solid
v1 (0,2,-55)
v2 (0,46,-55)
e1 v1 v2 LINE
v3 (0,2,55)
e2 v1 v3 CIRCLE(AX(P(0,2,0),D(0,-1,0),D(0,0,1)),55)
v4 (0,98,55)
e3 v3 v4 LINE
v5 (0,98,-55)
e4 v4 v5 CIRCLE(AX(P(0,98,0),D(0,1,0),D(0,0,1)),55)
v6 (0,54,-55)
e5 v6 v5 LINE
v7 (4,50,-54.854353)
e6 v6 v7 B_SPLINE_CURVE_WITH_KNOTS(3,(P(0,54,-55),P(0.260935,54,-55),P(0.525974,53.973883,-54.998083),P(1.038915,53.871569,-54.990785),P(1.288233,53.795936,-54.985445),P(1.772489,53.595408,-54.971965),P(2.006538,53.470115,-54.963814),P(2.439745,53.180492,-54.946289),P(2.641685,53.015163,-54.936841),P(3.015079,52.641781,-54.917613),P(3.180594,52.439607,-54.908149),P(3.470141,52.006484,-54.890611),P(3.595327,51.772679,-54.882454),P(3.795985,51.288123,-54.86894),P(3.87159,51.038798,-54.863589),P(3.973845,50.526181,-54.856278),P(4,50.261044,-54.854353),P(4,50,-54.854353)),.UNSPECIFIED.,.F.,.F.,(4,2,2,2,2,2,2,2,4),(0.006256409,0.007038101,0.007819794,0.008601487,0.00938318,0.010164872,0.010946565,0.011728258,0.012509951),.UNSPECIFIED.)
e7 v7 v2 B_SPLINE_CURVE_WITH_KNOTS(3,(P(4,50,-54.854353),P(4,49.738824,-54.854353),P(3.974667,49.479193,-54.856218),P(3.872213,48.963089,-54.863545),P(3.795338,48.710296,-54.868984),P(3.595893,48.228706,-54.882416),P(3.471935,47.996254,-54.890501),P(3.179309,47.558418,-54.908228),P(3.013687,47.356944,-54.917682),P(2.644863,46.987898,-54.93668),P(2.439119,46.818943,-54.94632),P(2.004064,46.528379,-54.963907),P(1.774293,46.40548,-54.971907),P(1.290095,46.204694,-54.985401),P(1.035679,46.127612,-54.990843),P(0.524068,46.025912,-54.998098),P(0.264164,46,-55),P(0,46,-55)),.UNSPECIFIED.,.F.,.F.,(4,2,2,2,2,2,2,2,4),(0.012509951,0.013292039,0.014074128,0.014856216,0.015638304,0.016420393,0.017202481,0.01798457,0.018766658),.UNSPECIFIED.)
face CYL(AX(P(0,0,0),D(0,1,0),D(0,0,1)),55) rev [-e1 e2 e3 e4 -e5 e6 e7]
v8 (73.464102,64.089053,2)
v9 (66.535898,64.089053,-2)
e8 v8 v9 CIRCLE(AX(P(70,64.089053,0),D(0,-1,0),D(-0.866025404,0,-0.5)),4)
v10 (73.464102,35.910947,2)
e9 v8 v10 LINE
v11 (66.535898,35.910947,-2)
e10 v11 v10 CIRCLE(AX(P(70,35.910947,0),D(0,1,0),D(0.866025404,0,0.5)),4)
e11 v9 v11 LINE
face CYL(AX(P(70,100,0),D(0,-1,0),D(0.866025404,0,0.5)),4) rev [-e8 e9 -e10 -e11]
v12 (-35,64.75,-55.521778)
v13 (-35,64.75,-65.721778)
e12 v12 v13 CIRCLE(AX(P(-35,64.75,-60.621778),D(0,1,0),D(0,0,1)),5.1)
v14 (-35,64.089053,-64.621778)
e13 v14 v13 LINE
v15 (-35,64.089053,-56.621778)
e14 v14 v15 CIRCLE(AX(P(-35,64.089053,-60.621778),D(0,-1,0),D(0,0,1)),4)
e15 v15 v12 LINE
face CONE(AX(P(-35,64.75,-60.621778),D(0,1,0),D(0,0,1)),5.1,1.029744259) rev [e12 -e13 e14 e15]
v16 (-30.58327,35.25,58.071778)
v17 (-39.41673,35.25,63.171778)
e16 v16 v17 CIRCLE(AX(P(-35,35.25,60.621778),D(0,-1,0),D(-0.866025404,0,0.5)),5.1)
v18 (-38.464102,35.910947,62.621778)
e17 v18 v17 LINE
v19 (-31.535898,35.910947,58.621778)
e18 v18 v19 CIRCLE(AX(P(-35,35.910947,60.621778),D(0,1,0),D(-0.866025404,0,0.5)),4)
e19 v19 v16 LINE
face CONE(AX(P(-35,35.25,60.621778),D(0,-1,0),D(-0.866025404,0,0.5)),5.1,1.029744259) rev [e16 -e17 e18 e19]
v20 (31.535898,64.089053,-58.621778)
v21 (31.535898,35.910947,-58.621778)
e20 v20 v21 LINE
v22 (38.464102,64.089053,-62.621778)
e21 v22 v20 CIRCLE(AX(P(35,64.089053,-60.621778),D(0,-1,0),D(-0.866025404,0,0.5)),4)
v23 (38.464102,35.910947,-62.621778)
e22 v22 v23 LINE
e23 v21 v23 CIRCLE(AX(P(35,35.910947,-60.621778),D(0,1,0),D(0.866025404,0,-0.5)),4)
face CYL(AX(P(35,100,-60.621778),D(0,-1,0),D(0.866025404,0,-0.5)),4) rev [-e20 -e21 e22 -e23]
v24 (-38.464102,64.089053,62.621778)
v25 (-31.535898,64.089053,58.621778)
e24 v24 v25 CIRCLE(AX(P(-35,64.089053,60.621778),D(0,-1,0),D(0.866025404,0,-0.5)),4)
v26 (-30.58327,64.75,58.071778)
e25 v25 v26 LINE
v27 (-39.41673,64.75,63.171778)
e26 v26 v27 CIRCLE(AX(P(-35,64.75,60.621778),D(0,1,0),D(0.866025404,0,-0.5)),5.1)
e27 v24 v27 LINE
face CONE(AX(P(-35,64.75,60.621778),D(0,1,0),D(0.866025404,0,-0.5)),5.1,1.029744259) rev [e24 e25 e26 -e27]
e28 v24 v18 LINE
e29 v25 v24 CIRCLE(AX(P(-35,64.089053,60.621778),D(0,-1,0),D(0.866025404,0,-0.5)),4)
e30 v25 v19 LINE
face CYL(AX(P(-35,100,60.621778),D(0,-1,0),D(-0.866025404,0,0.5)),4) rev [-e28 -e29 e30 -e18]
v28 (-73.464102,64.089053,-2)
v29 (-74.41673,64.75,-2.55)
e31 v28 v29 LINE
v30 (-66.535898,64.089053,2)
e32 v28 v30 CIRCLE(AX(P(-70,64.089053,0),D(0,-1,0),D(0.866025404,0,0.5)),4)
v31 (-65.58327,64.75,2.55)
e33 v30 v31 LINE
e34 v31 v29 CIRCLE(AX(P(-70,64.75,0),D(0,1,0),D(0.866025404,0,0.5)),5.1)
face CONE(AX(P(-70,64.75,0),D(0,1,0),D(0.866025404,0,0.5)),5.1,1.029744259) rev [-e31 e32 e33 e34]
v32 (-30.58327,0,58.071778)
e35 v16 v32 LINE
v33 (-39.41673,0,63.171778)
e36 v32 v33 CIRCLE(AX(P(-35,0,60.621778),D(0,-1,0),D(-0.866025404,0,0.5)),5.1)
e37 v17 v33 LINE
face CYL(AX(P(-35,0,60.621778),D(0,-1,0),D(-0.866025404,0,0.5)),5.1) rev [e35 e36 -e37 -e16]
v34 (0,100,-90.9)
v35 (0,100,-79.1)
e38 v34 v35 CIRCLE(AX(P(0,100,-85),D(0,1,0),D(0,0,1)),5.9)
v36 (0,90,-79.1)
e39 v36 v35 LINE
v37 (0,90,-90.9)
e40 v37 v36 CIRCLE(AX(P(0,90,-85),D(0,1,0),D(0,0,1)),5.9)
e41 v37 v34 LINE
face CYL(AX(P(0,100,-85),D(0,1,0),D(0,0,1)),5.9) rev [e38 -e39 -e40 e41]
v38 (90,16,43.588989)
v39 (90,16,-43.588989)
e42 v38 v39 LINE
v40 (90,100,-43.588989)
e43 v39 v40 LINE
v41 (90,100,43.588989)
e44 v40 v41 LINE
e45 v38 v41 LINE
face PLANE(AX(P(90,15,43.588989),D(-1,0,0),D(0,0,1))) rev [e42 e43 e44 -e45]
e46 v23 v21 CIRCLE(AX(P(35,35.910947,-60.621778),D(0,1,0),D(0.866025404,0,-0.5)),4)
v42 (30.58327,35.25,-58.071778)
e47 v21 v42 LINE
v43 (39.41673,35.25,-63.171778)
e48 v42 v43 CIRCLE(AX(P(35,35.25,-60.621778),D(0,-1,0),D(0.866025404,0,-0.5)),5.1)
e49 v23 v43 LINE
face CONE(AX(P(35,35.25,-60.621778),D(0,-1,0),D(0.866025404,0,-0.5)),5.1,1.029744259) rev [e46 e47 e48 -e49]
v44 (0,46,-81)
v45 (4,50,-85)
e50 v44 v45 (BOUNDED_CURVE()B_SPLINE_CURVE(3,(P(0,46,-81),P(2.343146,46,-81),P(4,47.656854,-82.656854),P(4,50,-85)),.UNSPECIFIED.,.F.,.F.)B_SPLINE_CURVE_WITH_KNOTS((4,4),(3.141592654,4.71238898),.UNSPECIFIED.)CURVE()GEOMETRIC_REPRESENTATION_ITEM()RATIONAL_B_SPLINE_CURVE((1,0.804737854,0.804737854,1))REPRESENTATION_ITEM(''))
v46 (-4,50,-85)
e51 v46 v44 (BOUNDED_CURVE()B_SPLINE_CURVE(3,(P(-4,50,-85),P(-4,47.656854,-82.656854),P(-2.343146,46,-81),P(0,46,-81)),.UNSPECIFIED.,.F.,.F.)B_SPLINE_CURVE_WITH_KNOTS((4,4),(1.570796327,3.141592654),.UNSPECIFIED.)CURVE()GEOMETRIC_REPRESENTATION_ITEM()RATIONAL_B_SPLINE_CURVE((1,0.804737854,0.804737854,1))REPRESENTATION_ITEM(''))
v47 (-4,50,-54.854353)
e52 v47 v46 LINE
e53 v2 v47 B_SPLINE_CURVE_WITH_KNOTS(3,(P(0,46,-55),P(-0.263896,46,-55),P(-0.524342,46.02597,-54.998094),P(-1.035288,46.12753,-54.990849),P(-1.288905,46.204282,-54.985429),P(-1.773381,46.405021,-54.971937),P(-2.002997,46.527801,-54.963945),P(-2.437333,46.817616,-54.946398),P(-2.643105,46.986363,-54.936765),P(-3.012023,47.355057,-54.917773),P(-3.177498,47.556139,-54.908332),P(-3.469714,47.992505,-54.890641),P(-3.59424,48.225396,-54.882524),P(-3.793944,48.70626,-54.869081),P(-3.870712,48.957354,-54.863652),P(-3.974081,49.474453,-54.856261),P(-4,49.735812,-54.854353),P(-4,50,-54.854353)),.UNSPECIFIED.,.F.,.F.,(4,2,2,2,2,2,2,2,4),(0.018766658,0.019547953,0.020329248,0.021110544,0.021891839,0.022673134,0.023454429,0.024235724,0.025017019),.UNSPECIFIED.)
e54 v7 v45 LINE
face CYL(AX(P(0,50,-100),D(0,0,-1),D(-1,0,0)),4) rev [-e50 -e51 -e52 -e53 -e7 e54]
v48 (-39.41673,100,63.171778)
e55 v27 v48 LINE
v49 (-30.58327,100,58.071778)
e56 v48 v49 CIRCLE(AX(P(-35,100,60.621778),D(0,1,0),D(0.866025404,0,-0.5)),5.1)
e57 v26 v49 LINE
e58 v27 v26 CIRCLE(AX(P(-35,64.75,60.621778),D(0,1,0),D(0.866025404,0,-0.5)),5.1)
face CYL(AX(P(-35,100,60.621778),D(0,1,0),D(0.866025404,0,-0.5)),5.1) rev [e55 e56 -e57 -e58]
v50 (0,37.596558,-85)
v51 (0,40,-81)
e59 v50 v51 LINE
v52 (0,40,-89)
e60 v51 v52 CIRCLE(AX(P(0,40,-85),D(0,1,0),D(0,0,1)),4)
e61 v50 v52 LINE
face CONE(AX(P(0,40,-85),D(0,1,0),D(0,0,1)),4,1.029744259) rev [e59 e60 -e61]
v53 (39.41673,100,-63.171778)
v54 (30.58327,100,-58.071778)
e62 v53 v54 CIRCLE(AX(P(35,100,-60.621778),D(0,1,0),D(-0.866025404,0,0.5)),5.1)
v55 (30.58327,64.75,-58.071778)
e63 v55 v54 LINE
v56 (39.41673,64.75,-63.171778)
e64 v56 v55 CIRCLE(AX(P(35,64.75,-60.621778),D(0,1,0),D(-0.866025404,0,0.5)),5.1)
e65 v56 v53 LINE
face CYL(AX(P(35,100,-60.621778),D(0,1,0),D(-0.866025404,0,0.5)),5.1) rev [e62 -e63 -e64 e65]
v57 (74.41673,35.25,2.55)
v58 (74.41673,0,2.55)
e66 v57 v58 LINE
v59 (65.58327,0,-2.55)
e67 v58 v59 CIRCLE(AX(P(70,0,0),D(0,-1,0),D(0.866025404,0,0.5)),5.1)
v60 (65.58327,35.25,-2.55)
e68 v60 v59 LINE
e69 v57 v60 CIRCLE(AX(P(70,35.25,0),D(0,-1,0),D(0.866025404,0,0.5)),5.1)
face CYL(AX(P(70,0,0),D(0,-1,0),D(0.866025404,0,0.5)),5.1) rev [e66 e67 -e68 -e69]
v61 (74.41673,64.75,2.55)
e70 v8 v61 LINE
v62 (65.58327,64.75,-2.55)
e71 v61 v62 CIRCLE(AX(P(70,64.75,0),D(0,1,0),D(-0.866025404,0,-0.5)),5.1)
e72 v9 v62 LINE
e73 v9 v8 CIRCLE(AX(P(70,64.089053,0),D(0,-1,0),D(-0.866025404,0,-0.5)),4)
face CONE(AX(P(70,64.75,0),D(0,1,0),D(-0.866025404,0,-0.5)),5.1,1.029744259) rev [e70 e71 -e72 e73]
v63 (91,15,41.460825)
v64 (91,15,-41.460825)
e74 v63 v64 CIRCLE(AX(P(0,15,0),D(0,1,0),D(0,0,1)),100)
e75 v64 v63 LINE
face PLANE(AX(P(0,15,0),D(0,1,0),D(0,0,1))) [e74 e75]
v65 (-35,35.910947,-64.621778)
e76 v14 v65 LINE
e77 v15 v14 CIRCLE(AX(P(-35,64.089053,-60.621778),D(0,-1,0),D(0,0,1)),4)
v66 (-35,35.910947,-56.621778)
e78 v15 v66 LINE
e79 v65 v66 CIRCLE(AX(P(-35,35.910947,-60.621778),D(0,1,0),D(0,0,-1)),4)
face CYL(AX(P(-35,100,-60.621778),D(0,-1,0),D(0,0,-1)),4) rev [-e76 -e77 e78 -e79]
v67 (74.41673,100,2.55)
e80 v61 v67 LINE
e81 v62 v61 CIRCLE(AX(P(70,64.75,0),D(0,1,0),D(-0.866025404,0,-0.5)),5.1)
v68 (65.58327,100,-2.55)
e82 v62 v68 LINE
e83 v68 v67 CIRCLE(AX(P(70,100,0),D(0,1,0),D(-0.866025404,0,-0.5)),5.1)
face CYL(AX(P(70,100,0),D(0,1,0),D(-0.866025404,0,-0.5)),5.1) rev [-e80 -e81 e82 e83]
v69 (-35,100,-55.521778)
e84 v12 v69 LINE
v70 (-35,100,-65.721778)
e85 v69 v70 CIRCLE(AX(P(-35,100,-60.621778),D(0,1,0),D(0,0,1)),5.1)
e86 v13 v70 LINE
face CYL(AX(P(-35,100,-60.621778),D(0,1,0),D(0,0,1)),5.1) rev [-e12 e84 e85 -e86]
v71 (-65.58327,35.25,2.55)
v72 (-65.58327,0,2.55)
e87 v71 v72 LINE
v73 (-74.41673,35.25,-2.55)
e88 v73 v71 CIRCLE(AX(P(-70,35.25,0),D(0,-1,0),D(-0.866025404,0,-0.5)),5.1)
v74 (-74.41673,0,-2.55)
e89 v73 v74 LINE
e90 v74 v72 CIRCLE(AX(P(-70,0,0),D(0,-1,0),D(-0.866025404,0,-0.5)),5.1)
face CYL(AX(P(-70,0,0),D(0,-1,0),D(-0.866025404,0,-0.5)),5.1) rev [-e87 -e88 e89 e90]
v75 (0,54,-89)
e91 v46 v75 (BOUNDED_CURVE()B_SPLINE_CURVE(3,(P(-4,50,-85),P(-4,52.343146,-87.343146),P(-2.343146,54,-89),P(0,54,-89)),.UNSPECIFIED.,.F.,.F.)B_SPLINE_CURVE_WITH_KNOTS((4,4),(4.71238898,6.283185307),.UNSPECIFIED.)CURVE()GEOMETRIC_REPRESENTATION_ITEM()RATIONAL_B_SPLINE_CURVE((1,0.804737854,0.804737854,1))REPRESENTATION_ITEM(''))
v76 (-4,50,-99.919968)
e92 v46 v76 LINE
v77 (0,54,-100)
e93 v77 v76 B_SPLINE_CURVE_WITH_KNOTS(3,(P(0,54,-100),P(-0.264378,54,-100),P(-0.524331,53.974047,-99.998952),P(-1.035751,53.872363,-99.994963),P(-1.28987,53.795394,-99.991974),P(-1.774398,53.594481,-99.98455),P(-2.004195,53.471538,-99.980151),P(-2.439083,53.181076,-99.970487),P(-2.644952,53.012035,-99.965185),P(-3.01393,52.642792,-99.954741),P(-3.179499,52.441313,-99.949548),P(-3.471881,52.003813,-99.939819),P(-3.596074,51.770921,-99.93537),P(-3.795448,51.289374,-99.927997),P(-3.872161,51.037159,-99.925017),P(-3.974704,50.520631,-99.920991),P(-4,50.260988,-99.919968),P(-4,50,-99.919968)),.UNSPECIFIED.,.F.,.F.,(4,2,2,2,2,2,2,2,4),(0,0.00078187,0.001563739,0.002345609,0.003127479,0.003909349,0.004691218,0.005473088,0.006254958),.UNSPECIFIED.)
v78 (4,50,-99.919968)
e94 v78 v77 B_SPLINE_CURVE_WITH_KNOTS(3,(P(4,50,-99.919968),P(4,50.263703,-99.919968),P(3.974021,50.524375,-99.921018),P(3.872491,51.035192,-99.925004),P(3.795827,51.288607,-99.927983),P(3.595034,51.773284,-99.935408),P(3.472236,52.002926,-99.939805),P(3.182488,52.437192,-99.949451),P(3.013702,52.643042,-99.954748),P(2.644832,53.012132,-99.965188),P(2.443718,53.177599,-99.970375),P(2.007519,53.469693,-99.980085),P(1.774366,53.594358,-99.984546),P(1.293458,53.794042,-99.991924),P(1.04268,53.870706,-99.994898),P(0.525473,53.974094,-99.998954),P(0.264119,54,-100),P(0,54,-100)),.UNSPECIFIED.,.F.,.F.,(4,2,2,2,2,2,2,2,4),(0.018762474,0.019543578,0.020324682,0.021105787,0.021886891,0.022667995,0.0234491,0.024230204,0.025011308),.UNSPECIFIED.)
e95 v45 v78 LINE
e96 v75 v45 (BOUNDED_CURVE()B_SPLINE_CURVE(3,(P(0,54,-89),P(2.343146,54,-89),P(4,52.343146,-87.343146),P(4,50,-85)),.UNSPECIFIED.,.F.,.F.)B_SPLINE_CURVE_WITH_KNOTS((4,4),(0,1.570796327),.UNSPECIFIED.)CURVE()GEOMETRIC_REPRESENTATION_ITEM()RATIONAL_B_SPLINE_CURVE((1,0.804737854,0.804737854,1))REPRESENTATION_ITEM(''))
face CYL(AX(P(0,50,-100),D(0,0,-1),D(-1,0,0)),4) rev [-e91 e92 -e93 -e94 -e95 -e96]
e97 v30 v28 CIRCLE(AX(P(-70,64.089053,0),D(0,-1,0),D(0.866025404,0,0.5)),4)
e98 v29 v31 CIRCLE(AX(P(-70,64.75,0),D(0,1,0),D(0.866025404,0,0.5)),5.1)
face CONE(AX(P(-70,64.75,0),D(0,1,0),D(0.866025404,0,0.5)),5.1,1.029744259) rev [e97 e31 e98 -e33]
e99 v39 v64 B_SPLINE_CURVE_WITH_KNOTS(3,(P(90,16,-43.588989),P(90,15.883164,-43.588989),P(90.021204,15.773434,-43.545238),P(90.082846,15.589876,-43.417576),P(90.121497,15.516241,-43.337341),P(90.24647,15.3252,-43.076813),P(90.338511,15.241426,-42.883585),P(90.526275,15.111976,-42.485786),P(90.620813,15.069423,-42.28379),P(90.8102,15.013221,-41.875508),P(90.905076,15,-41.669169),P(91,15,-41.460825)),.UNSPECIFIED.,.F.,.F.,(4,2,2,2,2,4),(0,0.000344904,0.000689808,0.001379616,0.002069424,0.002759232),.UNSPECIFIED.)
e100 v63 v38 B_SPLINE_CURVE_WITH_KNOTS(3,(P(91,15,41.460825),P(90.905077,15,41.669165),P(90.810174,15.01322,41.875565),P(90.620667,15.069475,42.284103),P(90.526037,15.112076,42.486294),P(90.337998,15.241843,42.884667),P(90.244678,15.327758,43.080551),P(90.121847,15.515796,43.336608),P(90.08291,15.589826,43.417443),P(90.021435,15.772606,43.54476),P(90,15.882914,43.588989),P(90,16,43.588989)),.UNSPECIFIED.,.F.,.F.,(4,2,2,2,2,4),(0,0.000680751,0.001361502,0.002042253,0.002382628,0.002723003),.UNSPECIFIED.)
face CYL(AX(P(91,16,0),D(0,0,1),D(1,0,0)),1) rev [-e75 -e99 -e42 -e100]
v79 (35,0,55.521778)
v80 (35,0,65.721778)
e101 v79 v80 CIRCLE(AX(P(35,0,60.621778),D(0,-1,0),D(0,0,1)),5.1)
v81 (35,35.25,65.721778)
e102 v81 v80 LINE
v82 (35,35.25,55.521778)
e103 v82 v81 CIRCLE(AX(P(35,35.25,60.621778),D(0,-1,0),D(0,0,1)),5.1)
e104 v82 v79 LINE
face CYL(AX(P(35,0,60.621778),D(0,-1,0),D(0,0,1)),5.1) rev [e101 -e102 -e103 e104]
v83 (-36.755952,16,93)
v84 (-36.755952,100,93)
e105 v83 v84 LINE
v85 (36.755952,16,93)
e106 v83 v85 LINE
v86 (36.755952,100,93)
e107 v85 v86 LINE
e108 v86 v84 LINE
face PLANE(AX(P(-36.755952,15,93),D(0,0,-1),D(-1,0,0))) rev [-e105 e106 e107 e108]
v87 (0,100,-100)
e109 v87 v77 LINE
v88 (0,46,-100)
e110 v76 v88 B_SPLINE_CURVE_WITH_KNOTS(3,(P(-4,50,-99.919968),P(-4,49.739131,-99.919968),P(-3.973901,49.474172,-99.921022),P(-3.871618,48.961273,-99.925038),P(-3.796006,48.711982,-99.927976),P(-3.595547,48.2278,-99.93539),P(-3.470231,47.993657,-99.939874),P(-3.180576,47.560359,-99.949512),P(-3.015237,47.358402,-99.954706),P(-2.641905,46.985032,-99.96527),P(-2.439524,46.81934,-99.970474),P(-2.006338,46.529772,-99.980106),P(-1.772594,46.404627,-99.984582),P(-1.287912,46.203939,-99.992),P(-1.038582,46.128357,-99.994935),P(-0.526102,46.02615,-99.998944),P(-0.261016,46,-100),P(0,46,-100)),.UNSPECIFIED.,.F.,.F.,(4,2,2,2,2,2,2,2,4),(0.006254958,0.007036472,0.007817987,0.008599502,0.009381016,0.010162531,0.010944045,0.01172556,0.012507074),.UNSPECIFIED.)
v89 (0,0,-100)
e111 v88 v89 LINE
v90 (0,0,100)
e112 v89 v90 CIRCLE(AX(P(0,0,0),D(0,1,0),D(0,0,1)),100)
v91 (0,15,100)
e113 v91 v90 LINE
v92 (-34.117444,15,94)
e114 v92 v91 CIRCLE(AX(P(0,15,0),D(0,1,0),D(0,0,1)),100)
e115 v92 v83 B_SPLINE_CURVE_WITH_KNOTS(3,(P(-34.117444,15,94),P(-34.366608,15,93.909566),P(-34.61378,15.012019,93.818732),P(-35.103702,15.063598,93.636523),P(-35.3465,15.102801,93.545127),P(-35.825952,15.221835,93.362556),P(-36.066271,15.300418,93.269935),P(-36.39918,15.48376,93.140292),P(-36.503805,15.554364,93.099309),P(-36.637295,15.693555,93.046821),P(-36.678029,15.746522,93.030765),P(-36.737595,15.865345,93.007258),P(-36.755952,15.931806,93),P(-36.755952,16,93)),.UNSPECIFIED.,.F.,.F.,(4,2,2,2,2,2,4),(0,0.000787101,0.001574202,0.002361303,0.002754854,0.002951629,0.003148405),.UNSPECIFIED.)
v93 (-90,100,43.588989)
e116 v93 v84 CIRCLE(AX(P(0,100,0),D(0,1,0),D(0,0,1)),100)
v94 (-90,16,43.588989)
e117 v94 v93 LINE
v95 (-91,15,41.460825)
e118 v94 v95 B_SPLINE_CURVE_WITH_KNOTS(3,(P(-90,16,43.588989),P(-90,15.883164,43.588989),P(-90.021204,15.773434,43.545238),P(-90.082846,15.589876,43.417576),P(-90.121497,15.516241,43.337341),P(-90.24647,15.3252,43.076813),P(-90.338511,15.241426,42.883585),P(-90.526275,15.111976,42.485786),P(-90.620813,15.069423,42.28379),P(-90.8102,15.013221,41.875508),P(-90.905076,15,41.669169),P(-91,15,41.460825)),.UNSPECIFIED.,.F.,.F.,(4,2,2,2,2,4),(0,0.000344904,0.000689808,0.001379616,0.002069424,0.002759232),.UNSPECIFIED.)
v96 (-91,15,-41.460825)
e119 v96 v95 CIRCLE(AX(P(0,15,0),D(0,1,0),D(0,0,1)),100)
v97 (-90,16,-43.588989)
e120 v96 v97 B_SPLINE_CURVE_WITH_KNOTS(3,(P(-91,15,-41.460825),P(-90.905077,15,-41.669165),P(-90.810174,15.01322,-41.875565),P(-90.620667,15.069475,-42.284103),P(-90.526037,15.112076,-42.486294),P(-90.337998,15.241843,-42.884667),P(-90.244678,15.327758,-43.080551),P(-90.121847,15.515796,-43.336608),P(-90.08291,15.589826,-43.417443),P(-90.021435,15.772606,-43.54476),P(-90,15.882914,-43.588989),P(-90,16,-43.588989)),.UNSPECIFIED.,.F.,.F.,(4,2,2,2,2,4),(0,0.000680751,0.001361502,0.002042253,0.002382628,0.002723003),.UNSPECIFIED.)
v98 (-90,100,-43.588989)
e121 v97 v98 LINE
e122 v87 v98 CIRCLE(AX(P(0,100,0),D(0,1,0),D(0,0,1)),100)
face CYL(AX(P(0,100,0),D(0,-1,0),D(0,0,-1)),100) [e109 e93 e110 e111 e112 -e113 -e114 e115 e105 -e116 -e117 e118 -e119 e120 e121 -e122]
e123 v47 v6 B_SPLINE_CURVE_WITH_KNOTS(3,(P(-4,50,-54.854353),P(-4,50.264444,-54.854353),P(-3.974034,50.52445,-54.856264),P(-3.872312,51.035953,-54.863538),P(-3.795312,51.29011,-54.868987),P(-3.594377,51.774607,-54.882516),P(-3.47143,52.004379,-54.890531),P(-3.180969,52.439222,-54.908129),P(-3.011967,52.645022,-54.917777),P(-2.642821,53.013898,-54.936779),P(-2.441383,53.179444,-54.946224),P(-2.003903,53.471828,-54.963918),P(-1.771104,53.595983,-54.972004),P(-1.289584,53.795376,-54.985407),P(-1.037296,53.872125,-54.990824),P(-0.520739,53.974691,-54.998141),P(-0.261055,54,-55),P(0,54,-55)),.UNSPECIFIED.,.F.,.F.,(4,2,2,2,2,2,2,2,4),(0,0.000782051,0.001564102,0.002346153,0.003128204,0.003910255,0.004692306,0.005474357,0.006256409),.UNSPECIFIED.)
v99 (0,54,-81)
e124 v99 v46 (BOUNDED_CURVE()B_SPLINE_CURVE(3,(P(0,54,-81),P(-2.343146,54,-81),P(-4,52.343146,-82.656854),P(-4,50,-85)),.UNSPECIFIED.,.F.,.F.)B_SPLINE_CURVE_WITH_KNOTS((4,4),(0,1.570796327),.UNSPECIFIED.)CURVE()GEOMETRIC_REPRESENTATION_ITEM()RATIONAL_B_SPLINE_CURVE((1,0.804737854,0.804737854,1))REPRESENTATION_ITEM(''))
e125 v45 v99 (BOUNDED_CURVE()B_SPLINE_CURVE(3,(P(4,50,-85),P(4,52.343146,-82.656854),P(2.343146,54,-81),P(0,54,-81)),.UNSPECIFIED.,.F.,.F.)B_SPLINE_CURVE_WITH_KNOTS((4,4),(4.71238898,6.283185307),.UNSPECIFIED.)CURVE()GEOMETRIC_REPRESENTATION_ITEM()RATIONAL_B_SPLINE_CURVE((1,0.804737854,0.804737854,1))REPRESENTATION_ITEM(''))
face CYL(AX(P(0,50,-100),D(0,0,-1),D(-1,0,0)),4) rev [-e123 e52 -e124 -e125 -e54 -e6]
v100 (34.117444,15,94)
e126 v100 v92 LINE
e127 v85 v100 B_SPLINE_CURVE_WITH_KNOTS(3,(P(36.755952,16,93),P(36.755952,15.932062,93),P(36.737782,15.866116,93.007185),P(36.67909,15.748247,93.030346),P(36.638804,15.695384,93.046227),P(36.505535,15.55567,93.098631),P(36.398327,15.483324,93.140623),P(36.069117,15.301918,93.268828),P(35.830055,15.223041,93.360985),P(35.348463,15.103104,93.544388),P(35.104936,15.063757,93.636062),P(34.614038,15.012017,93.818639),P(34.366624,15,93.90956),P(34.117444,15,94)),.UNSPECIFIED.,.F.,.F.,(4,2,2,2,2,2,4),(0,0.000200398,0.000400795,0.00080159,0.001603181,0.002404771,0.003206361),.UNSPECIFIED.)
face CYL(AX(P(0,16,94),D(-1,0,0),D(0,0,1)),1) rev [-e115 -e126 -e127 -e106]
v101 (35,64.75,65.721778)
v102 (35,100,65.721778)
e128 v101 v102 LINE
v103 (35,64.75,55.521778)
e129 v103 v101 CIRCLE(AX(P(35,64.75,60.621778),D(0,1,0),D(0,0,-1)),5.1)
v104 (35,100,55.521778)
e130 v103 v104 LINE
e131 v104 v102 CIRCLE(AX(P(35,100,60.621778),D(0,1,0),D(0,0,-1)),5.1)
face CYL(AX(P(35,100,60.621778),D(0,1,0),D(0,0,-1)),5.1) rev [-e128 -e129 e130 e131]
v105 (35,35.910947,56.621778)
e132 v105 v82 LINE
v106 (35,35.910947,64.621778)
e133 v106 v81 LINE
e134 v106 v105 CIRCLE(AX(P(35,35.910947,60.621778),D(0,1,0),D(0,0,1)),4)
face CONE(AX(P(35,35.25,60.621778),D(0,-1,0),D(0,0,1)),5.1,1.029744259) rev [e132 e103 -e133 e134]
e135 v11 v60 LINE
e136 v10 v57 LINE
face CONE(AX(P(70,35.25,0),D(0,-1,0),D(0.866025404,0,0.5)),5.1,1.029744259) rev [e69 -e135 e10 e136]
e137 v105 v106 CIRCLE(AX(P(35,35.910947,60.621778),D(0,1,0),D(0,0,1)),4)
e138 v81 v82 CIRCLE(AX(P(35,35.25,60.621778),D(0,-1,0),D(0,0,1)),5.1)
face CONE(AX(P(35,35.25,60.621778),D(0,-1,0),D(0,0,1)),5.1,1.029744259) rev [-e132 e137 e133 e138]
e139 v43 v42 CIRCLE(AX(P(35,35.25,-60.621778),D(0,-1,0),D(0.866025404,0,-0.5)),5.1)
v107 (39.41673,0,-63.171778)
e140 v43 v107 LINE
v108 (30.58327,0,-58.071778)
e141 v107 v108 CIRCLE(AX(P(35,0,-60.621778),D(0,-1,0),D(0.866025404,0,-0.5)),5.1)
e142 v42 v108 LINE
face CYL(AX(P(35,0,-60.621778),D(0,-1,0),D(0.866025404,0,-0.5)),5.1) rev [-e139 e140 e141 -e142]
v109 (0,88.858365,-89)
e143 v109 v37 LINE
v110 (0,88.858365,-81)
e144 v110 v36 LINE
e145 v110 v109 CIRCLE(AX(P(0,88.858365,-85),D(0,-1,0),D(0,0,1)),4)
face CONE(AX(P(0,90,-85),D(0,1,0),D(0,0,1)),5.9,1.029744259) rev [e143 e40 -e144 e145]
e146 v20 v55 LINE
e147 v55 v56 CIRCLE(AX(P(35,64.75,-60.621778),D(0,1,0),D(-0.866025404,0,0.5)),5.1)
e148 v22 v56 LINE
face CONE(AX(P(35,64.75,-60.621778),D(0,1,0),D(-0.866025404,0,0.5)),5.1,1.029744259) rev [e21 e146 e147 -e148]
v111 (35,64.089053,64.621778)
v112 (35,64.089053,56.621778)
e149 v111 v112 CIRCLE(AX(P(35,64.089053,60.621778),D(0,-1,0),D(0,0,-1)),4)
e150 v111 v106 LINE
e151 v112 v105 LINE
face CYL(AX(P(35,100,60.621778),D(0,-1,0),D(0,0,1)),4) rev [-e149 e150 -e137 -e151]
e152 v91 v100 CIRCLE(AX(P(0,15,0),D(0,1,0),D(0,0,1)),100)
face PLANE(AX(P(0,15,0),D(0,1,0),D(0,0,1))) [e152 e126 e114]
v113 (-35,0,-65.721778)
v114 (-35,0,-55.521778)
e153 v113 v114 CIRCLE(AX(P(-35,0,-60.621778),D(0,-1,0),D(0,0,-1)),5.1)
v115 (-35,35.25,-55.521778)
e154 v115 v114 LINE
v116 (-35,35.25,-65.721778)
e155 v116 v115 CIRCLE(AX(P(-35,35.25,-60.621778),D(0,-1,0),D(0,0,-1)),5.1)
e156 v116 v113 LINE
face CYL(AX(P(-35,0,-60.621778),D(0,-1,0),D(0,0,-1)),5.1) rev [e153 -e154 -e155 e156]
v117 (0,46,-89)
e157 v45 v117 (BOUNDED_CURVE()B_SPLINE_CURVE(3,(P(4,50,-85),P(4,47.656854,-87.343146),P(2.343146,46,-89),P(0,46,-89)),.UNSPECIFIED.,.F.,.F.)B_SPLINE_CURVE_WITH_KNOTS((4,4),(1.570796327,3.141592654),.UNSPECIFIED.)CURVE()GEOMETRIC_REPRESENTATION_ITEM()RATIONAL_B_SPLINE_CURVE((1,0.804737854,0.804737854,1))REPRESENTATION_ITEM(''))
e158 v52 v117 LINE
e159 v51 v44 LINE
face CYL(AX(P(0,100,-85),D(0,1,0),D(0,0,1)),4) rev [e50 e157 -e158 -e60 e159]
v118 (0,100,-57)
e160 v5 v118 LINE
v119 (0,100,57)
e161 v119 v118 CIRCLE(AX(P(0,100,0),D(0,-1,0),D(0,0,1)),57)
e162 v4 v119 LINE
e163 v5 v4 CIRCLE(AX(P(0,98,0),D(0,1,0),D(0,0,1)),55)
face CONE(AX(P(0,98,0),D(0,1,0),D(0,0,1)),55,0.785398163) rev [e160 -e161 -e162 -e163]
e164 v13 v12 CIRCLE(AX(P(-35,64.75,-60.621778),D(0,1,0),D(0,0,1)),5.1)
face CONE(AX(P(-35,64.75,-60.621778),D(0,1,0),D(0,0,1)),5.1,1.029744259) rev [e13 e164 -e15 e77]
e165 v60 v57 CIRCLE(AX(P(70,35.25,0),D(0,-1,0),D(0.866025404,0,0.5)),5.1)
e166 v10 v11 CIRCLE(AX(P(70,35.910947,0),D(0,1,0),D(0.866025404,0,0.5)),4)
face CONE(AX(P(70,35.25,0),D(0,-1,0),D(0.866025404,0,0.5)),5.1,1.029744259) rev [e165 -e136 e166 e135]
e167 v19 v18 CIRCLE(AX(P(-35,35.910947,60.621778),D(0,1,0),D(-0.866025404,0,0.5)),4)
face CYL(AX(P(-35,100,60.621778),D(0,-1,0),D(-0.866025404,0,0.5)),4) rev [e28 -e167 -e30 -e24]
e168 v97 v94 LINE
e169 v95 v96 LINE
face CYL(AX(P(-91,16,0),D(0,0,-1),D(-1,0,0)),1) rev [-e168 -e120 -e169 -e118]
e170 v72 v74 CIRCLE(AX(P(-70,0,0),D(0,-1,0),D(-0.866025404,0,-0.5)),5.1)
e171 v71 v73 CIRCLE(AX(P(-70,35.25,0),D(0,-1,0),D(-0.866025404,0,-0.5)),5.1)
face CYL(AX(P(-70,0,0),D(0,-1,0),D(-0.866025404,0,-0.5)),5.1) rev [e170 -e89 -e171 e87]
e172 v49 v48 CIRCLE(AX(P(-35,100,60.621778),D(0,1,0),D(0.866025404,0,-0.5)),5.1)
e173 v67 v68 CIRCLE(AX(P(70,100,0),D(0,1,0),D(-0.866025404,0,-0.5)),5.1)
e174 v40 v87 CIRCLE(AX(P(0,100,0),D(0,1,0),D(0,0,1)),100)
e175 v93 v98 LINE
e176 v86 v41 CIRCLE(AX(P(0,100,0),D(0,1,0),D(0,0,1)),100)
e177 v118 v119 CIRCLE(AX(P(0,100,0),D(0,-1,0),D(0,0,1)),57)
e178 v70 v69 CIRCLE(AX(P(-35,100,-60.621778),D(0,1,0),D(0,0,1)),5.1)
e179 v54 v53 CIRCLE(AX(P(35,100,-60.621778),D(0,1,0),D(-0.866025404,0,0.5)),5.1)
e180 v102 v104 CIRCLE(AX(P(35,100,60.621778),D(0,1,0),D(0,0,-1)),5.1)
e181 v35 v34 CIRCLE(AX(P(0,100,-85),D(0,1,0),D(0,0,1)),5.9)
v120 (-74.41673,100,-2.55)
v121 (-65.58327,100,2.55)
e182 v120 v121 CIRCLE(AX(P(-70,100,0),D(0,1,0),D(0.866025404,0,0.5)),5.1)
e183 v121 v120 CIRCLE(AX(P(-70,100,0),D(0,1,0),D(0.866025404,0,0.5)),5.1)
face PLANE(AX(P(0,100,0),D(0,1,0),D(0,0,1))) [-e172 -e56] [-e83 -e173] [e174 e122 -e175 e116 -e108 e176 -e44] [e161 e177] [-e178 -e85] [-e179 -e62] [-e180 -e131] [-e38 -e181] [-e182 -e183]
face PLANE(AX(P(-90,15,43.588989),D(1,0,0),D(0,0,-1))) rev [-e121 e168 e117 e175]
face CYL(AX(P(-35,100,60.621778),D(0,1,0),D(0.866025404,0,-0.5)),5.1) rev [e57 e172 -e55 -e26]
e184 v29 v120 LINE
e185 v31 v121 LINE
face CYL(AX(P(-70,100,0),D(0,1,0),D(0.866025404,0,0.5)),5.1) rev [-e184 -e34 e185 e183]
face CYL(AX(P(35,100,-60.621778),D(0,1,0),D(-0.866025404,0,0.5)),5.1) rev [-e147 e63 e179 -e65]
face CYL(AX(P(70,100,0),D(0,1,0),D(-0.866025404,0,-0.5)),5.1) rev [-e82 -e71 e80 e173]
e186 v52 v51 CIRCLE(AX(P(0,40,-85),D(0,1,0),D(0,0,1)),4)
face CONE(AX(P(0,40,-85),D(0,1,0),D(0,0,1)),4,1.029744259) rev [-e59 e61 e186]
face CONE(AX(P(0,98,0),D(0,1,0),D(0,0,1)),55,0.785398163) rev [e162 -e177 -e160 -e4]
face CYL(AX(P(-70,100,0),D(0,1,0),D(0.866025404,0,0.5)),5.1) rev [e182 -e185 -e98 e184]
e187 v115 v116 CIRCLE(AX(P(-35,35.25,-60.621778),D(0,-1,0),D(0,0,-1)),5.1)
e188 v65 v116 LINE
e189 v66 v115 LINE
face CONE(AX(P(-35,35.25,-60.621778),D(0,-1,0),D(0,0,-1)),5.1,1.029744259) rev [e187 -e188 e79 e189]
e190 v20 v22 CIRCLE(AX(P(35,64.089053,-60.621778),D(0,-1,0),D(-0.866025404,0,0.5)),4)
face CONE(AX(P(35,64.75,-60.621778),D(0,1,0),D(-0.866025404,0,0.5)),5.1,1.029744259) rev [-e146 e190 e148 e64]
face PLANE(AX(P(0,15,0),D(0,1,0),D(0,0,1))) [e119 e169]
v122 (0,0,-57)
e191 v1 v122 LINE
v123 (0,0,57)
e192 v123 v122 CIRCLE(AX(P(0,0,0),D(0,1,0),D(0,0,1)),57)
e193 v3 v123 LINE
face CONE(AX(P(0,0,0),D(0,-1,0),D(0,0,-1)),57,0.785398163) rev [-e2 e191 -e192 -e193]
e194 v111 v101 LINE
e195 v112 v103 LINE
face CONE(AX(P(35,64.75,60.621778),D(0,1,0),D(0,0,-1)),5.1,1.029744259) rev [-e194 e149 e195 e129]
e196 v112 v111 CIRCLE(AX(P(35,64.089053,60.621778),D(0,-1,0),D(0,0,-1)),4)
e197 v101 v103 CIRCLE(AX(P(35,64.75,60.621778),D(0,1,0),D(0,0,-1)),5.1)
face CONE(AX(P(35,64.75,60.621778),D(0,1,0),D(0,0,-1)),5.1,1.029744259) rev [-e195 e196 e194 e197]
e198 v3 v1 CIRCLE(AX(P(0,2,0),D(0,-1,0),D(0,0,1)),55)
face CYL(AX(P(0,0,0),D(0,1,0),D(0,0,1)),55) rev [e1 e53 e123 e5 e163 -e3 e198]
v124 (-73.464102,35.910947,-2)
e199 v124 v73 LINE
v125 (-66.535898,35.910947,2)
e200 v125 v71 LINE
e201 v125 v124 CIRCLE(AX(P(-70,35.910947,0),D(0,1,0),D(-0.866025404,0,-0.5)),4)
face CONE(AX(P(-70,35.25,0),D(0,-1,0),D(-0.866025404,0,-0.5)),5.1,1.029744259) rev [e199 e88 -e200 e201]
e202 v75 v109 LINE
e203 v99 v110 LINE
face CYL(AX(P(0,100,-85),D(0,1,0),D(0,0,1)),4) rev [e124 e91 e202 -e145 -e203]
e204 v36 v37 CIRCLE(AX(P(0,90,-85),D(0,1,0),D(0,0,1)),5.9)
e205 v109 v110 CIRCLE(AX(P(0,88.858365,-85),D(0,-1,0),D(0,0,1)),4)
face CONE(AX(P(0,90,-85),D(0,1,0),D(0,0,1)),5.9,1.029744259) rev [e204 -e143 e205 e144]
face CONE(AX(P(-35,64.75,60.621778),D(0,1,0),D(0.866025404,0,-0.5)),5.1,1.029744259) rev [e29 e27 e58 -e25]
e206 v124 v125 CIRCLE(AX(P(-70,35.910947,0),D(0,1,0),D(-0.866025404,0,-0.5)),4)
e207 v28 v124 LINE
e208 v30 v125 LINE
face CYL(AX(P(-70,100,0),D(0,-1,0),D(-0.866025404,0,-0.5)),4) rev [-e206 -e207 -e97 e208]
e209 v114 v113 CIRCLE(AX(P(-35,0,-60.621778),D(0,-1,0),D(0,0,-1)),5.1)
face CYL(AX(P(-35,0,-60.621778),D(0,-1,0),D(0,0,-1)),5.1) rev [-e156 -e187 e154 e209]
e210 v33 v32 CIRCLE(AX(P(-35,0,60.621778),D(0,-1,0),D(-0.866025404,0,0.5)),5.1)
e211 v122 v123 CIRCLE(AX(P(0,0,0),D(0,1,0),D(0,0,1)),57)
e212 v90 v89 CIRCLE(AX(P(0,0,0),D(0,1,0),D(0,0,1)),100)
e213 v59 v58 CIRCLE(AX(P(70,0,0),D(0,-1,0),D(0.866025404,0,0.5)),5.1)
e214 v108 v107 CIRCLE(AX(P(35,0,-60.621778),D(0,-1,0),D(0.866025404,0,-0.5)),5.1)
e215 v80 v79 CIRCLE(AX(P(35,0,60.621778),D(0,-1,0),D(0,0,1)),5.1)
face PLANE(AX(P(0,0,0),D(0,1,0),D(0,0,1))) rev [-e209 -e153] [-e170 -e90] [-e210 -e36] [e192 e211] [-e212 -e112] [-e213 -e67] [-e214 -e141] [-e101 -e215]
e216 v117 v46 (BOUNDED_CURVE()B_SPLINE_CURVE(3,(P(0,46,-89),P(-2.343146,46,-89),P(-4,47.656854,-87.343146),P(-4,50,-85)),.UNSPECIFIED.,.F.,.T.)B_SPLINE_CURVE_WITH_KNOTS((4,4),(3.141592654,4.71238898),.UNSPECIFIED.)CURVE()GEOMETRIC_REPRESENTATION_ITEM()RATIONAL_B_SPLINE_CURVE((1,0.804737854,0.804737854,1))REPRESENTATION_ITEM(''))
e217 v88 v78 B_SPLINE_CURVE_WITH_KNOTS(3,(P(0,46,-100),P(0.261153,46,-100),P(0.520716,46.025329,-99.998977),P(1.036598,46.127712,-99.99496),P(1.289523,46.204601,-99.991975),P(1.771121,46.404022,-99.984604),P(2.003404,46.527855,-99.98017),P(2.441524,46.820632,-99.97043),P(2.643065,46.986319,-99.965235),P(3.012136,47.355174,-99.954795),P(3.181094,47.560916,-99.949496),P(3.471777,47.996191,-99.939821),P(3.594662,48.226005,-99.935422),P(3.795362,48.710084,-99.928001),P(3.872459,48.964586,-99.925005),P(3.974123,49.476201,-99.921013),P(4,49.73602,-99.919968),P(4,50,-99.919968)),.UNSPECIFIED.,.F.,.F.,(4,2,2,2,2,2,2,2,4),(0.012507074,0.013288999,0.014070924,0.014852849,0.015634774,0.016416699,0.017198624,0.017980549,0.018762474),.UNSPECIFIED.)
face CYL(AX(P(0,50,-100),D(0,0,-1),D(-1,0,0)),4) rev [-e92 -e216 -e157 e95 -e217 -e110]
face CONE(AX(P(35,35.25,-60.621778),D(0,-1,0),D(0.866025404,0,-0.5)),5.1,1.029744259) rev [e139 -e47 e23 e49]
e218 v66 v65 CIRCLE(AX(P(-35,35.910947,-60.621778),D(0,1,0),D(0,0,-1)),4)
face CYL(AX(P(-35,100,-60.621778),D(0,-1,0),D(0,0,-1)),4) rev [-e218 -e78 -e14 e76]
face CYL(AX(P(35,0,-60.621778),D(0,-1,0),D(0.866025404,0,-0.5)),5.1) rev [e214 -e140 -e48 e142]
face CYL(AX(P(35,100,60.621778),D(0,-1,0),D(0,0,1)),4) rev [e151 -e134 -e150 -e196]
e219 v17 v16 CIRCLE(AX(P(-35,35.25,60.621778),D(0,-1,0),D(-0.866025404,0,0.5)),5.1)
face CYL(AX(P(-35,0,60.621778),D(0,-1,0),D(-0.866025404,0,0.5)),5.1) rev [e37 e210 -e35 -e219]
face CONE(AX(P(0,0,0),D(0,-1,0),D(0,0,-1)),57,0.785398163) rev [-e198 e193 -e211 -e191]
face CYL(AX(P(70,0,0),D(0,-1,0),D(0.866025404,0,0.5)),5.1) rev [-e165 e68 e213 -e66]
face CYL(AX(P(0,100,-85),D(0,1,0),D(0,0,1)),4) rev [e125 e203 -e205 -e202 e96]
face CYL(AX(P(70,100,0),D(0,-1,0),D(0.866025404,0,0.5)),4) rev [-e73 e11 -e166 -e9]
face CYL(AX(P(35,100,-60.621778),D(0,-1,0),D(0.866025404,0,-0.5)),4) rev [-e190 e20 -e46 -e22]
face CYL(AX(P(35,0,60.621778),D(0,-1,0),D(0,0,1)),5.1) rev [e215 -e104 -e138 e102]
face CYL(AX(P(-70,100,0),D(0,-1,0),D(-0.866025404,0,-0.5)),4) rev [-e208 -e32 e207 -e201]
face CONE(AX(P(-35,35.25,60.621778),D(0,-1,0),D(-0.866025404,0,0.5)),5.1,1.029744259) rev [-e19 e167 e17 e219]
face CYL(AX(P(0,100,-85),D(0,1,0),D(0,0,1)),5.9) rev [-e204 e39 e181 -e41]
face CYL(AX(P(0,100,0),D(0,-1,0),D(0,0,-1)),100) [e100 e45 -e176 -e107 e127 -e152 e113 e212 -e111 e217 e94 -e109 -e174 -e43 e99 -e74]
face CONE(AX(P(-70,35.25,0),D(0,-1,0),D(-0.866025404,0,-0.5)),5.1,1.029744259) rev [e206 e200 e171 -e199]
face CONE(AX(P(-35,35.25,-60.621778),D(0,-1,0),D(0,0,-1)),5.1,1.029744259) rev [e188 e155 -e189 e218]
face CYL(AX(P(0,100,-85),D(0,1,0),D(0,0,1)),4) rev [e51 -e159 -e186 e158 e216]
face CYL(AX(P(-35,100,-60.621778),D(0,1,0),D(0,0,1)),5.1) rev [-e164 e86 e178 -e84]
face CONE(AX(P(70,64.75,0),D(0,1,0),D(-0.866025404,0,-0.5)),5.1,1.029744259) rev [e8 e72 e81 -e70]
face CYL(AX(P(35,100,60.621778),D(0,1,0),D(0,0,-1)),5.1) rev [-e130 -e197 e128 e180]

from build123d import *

# Parameters (mm, degrees)
SKETCH1_R                    = 100
BOSS_EXTRUDE1_DEPTH          = 100
CUT_EXTRUDE1_START           = -85
CUT_EXTRUDE1_DEPTH           = 85
SKETCH3_R                    = 55
CUT_EXTRUDE2_DEPTH           = 174.205080757
CHAMFER1_SIZE                = 2
SKETCH10_R                   = 4
CUT_EXTRUDE3_DEPTH           = 174.205080757
CIRPATTERN1_COUNT            = 6
G1_4_TAPPED_HOLE1_D          = 11.8
G1_4_TAPPED_HOLE1_DEPTH      = 10
G1_4_TAPPED_HOLE1_TIP        = 3.545077652
F_8_0_8_DIAMETER_HOLE1_D     = 8
F_8_0_8_DIAMETER_HOLE1_DEPTH = 60
F_8_0_8_DIAMETER_HOLE1_TIP   = 2.403442476
F_8_0_8_DIAMETER_HOLE2_D     = 8
F_8_0_8_DIAMETER_HOLE2_DEPTH = 60
F_8_0_8_DIAMETER_HOLE2_TIP   = 2.403442476
FILLET1_R                    = 1


with BuildPart() as part:
    # Sketch1 → Boss-Extrude1 (new body)
    with BuildSketch(Plane(origin=(0, 0, 0), x_dir=(1, 0, 0), z_dir=(0, 1, 0))):
        with Locations(Location((0, 0, 0), (0, 0, 270))):
            Circle(SKETCH1_R)
    extrude(amount=BOSS_EXTRUDE1_DEPTH)

    # Sketch2 → Cut-Extrude1 (cut)
    with BuildSketch(Plane(origin=(0, 100, 0), x_dir=(1, 0, 0), z_dir=(0, 1, 0)).offset(CUT_EXTRUDE1_START)):
        with BuildLine():
            Line((-36.755951899, -93), (36.755951899, -93))
            ThreePointArc((36.755951899, -93), (0, -100), (-36.755951899, -93))
        make_face()
        with BuildLine():
            Line((-90, -43.588989435), (-90, 43.588989435))
            ThreePointArc((-90, 43.588989435), (-100, 0), (-90, -43.588989435))
        make_face()
        with BuildLine():
            Line((90, -43.588989435), (90, 43.588989435))
            ThreePointArc((90, 43.588989435), (100, 0), (90, -43.588989435))
        make_face()
    extrude(amount=CUT_EXTRUDE1_DEPTH, mode=Mode.SUBTRACT)

    # Sketch3 → Cut-Extrude2 (cut, through all)
    with BuildSketch(Plane(origin=(0, 100, 0), x_dir=(1, 0, 0), z_dir=(0, 1, 0))):
        with Locations(Location((0, 0, 0), (0, 0, 270))):
            Circle(SKETCH3_R)
    extrude(amount=-CUT_EXTRUDE2_DEPTH, mode=Mode.SUBTRACT)

    # Chamfer1
    chamfer1_edges = [part.edges().sort_by_distance(p)[0] for p in [
        (0, 0, -55),
        (0, 100, -55),
    ]]
    chamfer(chamfer1_edges, length=CHAMFER1_SIZE)

    # Sketch6 → M12 Tapped Hole1 (revolve, cut)
    with BuildSketch(Plane(origin=(-35, 100, -60.621778265), x_dir=(0, 0, 1), z_dir=(1, 0, 0))):
        Polygon((0, 0), (0, 38.314389157), (5.1, 35.25), (5.1, 0), align=None)
    m12_tapped_hole1 = revolve(axis=Axis((-35, 106.35, -60.621778265), (0, -1, 0)), mode=Mode.SUBTRACT)

    # Sketch9 → M12 Tapped Hole2 (revolve, cut)
    with BuildSketch(Plane(origin=(-35, 0, -60.621778265), x_dir=(0, 0, -1), z_dir=(1, 0, 0))):
        Polygon((0, 0), (0, 38.314389157), (5.1, 35.25), (5.1, 0), align=None)
    m12_tapped_hole2 = revolve(axis=Axis((-35, -6.35, -60.621778265), (0, 1, 0)), mode=Mode.SUBTRACT)

    # Sketch10 → Cut-Extrude3 (cut, through all)
    with BuildSketch(Plane.XZ):
        with Locations(Location((-35, -60.621778265, 0), (0, 0, 270))):
            Circle(SKETCH10_R)
    cut_extrude3 = extrude(amount=-CUT_EXTRUDE3_DEPTH, mode=Mode.SUBTRACT)

    # CirPattern1: M12 Tapped Hole1, M12 Tapped Hole2, Cut-Extrude3 ×6 about axis
    cirpattern1_axis = Axis((0, 0, 0), (0, 1, 0))
    add([m12_tapped_hole1.rotate(cirpattern1_axis, i * 360 / CIRPATTERN1_COUNT) for i in range(1, CIRPATTERN1_COUNT)], mode=Mode.SUBTRACT)
    add([m12_tapped_hole2.rotate(cirpattern1_axis, i * 360 / CIRPATTERN1_COUNT) for i in range(1, CIRPATTERN1_COUNT)], mode=Mode.SUBTRACT)
    add([cut_extrude3.rotate(cirpattern1_axis, i * 360 / CIRPATTERN1_COUNT) for i in range(1, CIRPATTERN1_COUNT)], mode=Mode.SUBTRACT)

    # G1/4 Tapped Hole1
    with Locations(Plane(origin=(0, 100, 0), x_dir=(1, 0, 0), z_dir=(0, 1, 0))):
        with Locations((0, 85)):
            Hole(G1_4_TAPPED_HOLE1_D / 2, depth=G1_4_TAPPED_HOLE1_DEPTH)
            with Locations((0, 0, -(G1_4_TAPPED_HOLE1_DEPTH + G1_4_TAPPED_HOLE1_TIP / 2))):  # 118° drill point
                Cone(0, G1_4_TAPPED_HOLE1_D / 2, G1_4_TAPPED_HOLE1_TIP, mode=Mode.SUBTRACT)

    # Ø8.0 (8) Diameter Hole1
    with Locations(Plane(origin=(0, 100, 0), x_dir=(1, 0, 0), z_dir=(0, 1, 0))):
        with Locations((0, 85)):
            Hole(F_8_0_8_DIAMETER_HOLE1_D / 2, depth=F_8_0_8_DIAMETER_HOLE1_DEPTH)
            with Locations((0, 0, -(F_8_0_8_DIAMETER_HOLE1_DEPTH + F_8_0_8_DIAMETER_HOLE1_TIP / 2))):  # 118° drill point
                Cone(0, F_8_0_8_DIAMETER_HOLE1_D / 2, F_8_0_8_DIAMETER_HOLE1_TIP, mode=Mode.SUBTRACT)

    # Ø8.0 (8) Diameter Hole2
    with Locations(Plane(origin=(0, 50, -100), x_dir=(-1, 0, 0), z_dir=(0, 0, -1))):
        with Locations((0, 0)):
            Hole(F_8_0_8_DIAMETER_HOLE2_D / 2, depth=F_8_0_8_DIAMETER_HOLE2_DEPTH)
            with Locations((0, 0, -(F_8_0_8_DIAMETER_HOLE2_DEPTH + F_8_0_8_DIAMETER_HOLE2_TIP / 2))):  # 118° drill point
                Cone(0, F_8_0_8_DIAMETER_HOLE2_D / 2, F_8_0_8_DIAMETER_HOLE2_TIP, mode=Mode.SUBTRACT)

    # Fillet1
    fillet1_edges = [part.edges().sort_by_distance(p)[0] for p in [
        (0, 15, 93),
        (-90, 15, 0),
        (90, 15, 0),
    ]]
    fillet(fillet1_edges, radius=FILLET1_R)


solid = part.part
